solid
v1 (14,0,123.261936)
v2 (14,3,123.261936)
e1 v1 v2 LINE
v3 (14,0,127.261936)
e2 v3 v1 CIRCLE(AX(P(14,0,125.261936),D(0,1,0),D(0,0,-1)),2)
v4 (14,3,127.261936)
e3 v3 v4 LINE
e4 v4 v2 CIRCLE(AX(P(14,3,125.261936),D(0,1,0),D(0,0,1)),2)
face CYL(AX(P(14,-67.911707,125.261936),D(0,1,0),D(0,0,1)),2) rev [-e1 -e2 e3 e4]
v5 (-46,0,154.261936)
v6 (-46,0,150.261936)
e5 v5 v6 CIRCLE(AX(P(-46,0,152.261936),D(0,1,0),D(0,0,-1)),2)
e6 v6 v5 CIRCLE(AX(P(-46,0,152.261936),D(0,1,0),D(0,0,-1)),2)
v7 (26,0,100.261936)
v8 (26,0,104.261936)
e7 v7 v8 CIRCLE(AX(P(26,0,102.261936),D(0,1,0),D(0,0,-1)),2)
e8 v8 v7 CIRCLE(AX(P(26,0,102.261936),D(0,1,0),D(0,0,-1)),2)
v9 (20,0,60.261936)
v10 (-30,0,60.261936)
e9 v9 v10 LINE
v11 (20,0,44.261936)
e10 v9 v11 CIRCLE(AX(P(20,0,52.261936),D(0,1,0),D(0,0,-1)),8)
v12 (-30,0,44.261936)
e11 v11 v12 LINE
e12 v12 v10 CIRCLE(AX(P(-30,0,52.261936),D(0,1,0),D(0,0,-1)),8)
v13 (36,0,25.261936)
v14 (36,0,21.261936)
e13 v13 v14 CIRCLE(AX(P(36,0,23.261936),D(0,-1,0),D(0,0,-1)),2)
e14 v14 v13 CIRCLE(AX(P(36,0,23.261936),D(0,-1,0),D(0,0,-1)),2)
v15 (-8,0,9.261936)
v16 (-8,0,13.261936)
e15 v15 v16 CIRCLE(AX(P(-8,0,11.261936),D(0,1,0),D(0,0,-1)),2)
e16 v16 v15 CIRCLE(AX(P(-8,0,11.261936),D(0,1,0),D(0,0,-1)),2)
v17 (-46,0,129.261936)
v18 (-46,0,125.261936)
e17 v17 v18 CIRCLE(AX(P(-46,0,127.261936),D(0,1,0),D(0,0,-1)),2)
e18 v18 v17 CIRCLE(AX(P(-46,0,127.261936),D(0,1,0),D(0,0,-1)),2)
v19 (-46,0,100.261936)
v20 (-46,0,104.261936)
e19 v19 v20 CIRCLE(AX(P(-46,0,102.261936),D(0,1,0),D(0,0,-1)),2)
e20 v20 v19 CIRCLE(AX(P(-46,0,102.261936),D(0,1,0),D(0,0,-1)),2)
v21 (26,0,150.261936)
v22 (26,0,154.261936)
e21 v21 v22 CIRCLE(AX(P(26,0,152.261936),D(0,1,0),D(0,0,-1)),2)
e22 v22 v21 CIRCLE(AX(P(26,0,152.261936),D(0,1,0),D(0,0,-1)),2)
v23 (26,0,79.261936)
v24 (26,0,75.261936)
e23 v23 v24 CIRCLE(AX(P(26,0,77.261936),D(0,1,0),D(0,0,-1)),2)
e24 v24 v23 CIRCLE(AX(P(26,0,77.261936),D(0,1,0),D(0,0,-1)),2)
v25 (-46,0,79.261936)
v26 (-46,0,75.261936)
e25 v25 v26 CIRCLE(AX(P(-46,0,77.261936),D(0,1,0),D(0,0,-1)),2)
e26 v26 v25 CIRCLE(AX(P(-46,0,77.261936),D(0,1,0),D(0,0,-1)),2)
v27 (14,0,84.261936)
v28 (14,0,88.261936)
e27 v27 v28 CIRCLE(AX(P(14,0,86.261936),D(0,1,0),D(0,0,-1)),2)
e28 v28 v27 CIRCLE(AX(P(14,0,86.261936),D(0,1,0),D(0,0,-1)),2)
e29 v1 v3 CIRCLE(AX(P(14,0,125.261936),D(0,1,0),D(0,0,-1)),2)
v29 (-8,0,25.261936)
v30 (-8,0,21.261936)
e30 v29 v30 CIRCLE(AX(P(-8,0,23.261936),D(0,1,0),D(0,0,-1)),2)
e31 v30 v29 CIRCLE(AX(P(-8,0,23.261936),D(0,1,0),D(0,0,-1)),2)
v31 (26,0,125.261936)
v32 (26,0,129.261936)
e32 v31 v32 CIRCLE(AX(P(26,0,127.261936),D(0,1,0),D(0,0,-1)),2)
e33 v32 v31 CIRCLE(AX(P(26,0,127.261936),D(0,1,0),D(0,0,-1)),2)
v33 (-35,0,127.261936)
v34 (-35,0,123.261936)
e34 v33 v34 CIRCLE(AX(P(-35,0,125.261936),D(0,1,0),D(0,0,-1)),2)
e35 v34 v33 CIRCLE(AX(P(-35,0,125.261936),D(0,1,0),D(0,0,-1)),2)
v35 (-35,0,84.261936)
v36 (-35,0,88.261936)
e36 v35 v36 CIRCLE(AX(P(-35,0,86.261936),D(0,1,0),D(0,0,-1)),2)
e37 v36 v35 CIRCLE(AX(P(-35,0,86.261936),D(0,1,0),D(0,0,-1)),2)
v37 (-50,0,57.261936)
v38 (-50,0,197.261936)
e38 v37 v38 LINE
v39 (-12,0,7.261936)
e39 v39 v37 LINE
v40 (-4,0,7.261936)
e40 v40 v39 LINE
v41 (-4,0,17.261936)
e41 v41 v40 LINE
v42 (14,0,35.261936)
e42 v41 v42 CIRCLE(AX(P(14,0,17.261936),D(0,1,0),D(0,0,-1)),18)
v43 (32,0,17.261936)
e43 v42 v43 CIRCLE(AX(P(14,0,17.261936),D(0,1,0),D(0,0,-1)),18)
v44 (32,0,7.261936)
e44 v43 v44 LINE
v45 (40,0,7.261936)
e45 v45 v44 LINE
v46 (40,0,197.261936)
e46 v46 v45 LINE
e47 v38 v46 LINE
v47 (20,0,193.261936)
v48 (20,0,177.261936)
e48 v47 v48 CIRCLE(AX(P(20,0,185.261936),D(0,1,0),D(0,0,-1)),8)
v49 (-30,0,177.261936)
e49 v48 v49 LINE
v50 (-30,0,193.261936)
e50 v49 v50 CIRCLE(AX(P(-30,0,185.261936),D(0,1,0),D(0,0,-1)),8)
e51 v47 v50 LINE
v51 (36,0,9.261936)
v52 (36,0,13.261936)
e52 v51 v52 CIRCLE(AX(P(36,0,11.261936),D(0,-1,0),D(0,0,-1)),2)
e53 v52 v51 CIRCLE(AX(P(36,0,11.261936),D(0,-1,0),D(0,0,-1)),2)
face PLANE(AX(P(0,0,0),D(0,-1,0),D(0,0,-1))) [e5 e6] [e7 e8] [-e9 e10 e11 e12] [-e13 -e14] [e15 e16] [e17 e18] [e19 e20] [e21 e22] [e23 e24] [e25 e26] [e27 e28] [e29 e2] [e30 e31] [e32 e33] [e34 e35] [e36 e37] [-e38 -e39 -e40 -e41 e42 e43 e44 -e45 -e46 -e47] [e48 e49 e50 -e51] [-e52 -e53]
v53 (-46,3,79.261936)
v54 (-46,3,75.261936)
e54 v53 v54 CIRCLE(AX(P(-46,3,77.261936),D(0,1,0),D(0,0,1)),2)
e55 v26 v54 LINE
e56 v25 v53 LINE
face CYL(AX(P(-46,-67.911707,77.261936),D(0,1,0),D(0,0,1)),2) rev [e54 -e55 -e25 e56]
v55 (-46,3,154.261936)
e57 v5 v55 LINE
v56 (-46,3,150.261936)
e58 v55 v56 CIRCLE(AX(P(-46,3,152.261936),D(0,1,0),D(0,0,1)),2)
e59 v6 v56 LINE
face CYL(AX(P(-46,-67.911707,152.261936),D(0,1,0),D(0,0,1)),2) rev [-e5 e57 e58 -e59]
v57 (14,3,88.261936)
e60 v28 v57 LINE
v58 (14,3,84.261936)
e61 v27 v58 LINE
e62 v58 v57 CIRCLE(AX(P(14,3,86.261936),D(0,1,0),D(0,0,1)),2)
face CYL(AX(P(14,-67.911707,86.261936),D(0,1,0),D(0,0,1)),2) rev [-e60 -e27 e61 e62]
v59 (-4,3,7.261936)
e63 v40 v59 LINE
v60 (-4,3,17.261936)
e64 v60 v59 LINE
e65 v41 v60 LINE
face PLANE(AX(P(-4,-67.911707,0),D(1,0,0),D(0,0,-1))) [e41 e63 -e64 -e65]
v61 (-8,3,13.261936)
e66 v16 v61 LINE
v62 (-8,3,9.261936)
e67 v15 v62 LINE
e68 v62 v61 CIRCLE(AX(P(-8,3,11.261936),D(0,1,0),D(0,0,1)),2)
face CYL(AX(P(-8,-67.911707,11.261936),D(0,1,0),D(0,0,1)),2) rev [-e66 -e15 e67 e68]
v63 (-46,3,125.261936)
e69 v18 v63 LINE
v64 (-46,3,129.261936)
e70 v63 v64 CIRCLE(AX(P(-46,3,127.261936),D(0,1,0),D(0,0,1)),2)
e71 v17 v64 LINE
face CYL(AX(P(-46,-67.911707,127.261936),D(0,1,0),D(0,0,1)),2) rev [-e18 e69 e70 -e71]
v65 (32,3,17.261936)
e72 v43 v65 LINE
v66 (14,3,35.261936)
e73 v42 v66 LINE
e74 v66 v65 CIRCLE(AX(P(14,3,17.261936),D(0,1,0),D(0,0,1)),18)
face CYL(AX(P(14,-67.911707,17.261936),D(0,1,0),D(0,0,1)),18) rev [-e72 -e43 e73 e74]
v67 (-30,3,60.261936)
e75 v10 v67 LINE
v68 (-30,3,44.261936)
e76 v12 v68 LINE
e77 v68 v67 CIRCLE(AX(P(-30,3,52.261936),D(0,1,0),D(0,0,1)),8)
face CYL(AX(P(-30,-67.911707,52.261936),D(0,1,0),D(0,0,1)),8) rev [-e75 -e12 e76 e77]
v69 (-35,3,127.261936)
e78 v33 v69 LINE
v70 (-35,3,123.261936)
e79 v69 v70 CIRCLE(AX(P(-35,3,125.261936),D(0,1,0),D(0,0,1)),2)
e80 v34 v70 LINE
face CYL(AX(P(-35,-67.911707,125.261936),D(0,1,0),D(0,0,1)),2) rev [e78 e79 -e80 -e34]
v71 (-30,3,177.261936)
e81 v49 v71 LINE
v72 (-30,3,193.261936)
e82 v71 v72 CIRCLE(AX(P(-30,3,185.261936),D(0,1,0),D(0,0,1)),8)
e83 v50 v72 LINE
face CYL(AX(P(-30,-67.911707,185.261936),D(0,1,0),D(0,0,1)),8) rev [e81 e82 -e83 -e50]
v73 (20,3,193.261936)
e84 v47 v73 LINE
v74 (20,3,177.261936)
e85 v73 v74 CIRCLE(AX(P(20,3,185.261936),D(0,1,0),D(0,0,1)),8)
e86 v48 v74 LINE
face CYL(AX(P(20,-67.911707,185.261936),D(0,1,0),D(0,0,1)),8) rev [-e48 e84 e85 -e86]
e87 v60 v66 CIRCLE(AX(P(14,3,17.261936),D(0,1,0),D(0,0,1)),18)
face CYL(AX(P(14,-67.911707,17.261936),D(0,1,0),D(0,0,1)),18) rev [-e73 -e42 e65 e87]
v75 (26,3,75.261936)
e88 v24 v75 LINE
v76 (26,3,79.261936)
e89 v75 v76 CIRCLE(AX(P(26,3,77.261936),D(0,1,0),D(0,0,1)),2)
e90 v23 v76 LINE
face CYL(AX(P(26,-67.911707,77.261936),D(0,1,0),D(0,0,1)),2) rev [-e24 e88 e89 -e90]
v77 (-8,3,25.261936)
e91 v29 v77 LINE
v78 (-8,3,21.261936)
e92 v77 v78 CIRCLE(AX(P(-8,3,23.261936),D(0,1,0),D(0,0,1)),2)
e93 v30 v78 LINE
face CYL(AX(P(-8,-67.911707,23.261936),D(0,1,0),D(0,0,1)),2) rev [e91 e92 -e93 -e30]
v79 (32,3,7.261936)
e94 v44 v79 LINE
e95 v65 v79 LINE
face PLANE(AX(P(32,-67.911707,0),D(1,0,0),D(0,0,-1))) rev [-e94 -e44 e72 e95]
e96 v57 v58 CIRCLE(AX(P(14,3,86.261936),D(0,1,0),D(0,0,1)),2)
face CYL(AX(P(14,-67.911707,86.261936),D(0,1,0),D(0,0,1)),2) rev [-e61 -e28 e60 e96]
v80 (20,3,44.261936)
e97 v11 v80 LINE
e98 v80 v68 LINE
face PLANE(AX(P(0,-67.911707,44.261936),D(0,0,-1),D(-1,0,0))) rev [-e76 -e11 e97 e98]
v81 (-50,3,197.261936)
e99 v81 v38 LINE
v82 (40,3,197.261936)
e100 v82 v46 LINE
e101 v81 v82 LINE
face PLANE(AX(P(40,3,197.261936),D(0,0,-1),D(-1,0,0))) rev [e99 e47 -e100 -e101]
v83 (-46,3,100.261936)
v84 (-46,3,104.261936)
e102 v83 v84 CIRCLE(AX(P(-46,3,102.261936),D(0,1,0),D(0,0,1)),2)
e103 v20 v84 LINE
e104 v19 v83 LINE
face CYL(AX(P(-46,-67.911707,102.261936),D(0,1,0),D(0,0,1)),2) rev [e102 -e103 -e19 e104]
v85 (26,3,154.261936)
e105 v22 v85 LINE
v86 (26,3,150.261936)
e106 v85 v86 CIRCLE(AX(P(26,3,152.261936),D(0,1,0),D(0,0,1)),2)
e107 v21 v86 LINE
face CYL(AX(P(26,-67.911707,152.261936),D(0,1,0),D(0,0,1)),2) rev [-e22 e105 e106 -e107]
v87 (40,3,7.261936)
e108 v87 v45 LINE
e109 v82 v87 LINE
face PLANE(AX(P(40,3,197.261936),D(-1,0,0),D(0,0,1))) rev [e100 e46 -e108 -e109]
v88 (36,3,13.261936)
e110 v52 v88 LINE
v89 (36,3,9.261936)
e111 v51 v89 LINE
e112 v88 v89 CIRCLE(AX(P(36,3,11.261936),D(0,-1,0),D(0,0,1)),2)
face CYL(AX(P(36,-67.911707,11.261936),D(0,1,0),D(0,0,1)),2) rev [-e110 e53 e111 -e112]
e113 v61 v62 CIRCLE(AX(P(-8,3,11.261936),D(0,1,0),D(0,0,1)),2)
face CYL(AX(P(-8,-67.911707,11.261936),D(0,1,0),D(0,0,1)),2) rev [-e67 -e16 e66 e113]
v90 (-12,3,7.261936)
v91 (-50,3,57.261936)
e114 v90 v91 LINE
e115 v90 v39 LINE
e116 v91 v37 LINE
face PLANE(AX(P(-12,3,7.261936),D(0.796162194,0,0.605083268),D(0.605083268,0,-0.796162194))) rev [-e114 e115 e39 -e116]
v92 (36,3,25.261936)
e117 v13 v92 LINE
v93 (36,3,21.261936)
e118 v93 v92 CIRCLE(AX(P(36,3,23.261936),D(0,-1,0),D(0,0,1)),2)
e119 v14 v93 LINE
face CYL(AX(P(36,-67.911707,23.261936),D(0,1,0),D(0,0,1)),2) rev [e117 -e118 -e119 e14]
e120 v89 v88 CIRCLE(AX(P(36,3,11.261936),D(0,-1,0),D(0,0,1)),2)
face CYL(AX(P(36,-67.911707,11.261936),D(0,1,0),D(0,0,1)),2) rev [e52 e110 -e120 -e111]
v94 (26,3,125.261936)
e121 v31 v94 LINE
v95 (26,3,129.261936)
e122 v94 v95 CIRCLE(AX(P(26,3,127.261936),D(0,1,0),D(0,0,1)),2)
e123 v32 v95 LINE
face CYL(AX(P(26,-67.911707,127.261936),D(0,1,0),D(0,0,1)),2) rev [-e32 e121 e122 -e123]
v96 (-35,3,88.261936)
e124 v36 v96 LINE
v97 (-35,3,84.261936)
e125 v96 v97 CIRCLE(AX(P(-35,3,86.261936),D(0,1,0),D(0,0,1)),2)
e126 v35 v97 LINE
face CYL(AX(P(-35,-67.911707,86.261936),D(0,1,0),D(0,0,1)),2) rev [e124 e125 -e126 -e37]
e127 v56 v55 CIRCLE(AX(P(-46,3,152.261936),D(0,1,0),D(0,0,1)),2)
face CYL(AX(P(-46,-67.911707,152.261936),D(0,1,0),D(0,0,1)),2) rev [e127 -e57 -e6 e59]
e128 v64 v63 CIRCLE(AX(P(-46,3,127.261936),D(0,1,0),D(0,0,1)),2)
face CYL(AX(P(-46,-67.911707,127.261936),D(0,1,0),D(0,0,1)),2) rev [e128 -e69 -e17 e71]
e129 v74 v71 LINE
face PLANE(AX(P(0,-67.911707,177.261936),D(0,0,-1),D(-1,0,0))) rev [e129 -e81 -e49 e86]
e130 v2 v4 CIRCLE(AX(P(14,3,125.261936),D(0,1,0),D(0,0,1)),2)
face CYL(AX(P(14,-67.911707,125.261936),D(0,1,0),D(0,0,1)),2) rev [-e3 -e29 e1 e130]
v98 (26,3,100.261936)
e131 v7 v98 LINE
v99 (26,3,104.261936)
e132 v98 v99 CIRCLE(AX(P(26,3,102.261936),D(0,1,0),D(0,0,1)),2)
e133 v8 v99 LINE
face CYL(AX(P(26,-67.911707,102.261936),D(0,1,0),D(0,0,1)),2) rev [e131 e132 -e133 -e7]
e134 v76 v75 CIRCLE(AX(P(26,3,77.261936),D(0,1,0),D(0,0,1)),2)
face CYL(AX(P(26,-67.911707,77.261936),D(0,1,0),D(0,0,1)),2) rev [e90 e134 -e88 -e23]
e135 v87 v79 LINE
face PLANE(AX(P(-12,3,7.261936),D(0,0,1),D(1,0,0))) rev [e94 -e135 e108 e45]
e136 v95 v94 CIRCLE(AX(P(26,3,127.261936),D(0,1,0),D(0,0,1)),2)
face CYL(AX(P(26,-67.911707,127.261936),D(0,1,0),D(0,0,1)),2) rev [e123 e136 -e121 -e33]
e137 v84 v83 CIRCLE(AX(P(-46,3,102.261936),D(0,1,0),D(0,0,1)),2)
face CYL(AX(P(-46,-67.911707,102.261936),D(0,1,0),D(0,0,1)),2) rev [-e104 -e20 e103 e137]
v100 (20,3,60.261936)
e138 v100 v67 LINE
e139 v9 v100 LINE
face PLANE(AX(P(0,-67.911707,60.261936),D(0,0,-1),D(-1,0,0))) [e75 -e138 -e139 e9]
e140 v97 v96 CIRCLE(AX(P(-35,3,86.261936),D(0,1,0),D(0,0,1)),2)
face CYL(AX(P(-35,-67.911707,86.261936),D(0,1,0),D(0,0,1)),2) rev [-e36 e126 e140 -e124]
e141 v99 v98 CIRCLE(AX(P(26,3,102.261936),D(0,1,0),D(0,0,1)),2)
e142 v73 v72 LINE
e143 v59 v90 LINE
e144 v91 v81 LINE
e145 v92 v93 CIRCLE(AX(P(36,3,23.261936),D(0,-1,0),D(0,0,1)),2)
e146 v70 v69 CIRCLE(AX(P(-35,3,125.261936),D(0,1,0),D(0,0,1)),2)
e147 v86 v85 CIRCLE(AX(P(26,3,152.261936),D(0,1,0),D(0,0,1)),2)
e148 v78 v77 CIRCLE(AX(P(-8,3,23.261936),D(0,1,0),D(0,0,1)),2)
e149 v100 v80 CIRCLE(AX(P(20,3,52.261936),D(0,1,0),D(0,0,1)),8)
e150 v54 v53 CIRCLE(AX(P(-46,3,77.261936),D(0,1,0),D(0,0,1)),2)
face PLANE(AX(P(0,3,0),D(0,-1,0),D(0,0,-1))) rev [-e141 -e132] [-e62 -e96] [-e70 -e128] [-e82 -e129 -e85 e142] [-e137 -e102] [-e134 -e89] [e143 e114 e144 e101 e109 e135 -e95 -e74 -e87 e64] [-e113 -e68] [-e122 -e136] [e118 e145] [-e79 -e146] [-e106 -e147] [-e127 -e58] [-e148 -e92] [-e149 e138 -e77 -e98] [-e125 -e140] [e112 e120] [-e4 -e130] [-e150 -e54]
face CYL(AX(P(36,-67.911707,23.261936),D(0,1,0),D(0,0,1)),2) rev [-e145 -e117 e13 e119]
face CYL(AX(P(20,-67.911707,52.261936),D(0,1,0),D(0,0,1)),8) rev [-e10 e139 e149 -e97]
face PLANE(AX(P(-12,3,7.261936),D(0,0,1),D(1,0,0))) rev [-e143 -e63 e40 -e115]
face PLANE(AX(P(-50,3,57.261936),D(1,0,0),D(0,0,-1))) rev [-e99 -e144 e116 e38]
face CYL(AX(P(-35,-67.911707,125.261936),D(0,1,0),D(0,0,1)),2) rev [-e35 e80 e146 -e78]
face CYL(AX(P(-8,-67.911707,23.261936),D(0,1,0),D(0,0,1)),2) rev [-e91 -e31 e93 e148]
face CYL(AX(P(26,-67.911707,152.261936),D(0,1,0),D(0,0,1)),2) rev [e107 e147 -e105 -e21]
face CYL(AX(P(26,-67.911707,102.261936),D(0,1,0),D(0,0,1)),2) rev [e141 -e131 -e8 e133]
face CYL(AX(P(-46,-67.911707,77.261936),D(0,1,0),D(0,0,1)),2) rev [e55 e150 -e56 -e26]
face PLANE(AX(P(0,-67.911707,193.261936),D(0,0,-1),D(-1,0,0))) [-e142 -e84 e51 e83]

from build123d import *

# Parameters (mm, degrees)
BOSS_EXTRUDE1_DEPTH = 3
SKETCH2_R           = 2
CUT_EXTRUDE1_DEPTH  = 3


with BuildPart() as part:
    # Sketch1 → Boss-Extrude1 (new body)
    with BuildSketch(Plane(origin=(0, 0, 0), x_dir=(1, 0, 0), z_dir=(0, 1, 0))):
        Polygon((-12, -7.26193593), (40, -7.26193593), (40, -197.26193593), (-50, -197.26193593), (-50, -57.26193593), align=None)
    extrude(amount=BOSS_EXTRUDE1_DEPTH)

    # Sketch2 → Cut-Extrude1 (cut)
    with BuildSketch(Plane(origin=(0, 3, 0), x_dir=(1, 0, 0), z_dir=(0, 1, 0))):
        with BuildLine():
            Line((-30, -193.26193593), (20, -193.26193593))
            ThreePointArc((20, -193.26193593), (28, -185.26193593), (20, -177.26193593))
            Line((20, -177.26193593), (-30, -177.26193593))
            ThreePointArc((-30, -177.26193593), (-38, -185.26193593), (-30, -193.26193593))
        make_face()
        with BuildLine():
            Line((-30, -60.26193593), (20, -60.26193593))
            ThreePointArc((20, -60.26193593), (28, -52.26193593), (20, -44.26193593))
            Line((20, -44.26193593), (-30, -44.26193593))
            ThreePointArc((-30, -44.26193593), (-38, -52.26193593), (-30, -60.26193593))
        make_face()
        with BuildLine():
            ThreePointArc((-4, -17.26193593), (14, -35.26193593), (32, -17.26193593))
            Line((32, -17.26193593), (32, -7.26193593))
            Line((32, -7.26193593), (-4, -7.26193593))
            Line((-4, -7.26193593), (-4, -17.26193593))
        make_face()
        with Locations(Location((-46, -152.26193593, 0), (0, 0, 270))):
            Circle(SKETCH2_R)
        with Locations(Location((-46, -77.26193593, 0), (0, 0, 270))):
            Circle(SKETCH2_R)
        with Locations(Location((-46, -127.26193593, 0), (0, 0, 270))):
            Circle(SKETCH2_R)
        with Locations(Location((-46, -102.26193593, 0), (0, 0, 270))):
            Circle(SKETCH2_R)
        with Locations(Location((-8, -11.26193593, 0), (0, 0, 270))):
            Circle(SKETCH2_R)
        with Locations(Location((-8, -23.26193593, 0), (0, 0, 270))):
            Circle(SKETCH2_R)
        with Locations(Location((26, -152.26193593, 0), (0, 0, 270))):
            Circle(SKETCH2_R)
        with Locations(Location((26, -102.26193593, 0), (0, 0, 270))):
            Circle(SKETCH2_R)
        with Locations(Location((26, -127.26193593, 0), (0, 0, 270))):
            Circle(SKETCH2_R)
        with Locations(Location((26, -77.26193593, 0), (0, 0, 270))):
            Circle(SKETCH2_R)
        with Locations(Location((36, -23.26193593, 0), (0, 0, 270))):
            Circle(SKETCH2_R)
        with Locations(Location((36, -11.26193593, 0), (0, 0, 270))):
            Circle(SKETCH2_R)
        with Locations(Location((-35, -86.26193593, 0), (0, 0, 270))):
            Circle(SKETCH2_R)
        with Locations(Location((-35, -125.26193593, 0), (0, 0, 270))):
            Circle(SKETCH2_R)
        with Locations(Location((14, -86.26193593, 0), (0, 0, 270))):
            Circle(SKETCH2_R)
        with Locations(Location((14, -125.26193593, 0), (0, 0, 270))):
            Circle(SKETCH2_R)
    extrude(amount=-CUT_EXTRUDE1_DEPTH, mode=Mode.SUBTRACT)


solid = part.part
